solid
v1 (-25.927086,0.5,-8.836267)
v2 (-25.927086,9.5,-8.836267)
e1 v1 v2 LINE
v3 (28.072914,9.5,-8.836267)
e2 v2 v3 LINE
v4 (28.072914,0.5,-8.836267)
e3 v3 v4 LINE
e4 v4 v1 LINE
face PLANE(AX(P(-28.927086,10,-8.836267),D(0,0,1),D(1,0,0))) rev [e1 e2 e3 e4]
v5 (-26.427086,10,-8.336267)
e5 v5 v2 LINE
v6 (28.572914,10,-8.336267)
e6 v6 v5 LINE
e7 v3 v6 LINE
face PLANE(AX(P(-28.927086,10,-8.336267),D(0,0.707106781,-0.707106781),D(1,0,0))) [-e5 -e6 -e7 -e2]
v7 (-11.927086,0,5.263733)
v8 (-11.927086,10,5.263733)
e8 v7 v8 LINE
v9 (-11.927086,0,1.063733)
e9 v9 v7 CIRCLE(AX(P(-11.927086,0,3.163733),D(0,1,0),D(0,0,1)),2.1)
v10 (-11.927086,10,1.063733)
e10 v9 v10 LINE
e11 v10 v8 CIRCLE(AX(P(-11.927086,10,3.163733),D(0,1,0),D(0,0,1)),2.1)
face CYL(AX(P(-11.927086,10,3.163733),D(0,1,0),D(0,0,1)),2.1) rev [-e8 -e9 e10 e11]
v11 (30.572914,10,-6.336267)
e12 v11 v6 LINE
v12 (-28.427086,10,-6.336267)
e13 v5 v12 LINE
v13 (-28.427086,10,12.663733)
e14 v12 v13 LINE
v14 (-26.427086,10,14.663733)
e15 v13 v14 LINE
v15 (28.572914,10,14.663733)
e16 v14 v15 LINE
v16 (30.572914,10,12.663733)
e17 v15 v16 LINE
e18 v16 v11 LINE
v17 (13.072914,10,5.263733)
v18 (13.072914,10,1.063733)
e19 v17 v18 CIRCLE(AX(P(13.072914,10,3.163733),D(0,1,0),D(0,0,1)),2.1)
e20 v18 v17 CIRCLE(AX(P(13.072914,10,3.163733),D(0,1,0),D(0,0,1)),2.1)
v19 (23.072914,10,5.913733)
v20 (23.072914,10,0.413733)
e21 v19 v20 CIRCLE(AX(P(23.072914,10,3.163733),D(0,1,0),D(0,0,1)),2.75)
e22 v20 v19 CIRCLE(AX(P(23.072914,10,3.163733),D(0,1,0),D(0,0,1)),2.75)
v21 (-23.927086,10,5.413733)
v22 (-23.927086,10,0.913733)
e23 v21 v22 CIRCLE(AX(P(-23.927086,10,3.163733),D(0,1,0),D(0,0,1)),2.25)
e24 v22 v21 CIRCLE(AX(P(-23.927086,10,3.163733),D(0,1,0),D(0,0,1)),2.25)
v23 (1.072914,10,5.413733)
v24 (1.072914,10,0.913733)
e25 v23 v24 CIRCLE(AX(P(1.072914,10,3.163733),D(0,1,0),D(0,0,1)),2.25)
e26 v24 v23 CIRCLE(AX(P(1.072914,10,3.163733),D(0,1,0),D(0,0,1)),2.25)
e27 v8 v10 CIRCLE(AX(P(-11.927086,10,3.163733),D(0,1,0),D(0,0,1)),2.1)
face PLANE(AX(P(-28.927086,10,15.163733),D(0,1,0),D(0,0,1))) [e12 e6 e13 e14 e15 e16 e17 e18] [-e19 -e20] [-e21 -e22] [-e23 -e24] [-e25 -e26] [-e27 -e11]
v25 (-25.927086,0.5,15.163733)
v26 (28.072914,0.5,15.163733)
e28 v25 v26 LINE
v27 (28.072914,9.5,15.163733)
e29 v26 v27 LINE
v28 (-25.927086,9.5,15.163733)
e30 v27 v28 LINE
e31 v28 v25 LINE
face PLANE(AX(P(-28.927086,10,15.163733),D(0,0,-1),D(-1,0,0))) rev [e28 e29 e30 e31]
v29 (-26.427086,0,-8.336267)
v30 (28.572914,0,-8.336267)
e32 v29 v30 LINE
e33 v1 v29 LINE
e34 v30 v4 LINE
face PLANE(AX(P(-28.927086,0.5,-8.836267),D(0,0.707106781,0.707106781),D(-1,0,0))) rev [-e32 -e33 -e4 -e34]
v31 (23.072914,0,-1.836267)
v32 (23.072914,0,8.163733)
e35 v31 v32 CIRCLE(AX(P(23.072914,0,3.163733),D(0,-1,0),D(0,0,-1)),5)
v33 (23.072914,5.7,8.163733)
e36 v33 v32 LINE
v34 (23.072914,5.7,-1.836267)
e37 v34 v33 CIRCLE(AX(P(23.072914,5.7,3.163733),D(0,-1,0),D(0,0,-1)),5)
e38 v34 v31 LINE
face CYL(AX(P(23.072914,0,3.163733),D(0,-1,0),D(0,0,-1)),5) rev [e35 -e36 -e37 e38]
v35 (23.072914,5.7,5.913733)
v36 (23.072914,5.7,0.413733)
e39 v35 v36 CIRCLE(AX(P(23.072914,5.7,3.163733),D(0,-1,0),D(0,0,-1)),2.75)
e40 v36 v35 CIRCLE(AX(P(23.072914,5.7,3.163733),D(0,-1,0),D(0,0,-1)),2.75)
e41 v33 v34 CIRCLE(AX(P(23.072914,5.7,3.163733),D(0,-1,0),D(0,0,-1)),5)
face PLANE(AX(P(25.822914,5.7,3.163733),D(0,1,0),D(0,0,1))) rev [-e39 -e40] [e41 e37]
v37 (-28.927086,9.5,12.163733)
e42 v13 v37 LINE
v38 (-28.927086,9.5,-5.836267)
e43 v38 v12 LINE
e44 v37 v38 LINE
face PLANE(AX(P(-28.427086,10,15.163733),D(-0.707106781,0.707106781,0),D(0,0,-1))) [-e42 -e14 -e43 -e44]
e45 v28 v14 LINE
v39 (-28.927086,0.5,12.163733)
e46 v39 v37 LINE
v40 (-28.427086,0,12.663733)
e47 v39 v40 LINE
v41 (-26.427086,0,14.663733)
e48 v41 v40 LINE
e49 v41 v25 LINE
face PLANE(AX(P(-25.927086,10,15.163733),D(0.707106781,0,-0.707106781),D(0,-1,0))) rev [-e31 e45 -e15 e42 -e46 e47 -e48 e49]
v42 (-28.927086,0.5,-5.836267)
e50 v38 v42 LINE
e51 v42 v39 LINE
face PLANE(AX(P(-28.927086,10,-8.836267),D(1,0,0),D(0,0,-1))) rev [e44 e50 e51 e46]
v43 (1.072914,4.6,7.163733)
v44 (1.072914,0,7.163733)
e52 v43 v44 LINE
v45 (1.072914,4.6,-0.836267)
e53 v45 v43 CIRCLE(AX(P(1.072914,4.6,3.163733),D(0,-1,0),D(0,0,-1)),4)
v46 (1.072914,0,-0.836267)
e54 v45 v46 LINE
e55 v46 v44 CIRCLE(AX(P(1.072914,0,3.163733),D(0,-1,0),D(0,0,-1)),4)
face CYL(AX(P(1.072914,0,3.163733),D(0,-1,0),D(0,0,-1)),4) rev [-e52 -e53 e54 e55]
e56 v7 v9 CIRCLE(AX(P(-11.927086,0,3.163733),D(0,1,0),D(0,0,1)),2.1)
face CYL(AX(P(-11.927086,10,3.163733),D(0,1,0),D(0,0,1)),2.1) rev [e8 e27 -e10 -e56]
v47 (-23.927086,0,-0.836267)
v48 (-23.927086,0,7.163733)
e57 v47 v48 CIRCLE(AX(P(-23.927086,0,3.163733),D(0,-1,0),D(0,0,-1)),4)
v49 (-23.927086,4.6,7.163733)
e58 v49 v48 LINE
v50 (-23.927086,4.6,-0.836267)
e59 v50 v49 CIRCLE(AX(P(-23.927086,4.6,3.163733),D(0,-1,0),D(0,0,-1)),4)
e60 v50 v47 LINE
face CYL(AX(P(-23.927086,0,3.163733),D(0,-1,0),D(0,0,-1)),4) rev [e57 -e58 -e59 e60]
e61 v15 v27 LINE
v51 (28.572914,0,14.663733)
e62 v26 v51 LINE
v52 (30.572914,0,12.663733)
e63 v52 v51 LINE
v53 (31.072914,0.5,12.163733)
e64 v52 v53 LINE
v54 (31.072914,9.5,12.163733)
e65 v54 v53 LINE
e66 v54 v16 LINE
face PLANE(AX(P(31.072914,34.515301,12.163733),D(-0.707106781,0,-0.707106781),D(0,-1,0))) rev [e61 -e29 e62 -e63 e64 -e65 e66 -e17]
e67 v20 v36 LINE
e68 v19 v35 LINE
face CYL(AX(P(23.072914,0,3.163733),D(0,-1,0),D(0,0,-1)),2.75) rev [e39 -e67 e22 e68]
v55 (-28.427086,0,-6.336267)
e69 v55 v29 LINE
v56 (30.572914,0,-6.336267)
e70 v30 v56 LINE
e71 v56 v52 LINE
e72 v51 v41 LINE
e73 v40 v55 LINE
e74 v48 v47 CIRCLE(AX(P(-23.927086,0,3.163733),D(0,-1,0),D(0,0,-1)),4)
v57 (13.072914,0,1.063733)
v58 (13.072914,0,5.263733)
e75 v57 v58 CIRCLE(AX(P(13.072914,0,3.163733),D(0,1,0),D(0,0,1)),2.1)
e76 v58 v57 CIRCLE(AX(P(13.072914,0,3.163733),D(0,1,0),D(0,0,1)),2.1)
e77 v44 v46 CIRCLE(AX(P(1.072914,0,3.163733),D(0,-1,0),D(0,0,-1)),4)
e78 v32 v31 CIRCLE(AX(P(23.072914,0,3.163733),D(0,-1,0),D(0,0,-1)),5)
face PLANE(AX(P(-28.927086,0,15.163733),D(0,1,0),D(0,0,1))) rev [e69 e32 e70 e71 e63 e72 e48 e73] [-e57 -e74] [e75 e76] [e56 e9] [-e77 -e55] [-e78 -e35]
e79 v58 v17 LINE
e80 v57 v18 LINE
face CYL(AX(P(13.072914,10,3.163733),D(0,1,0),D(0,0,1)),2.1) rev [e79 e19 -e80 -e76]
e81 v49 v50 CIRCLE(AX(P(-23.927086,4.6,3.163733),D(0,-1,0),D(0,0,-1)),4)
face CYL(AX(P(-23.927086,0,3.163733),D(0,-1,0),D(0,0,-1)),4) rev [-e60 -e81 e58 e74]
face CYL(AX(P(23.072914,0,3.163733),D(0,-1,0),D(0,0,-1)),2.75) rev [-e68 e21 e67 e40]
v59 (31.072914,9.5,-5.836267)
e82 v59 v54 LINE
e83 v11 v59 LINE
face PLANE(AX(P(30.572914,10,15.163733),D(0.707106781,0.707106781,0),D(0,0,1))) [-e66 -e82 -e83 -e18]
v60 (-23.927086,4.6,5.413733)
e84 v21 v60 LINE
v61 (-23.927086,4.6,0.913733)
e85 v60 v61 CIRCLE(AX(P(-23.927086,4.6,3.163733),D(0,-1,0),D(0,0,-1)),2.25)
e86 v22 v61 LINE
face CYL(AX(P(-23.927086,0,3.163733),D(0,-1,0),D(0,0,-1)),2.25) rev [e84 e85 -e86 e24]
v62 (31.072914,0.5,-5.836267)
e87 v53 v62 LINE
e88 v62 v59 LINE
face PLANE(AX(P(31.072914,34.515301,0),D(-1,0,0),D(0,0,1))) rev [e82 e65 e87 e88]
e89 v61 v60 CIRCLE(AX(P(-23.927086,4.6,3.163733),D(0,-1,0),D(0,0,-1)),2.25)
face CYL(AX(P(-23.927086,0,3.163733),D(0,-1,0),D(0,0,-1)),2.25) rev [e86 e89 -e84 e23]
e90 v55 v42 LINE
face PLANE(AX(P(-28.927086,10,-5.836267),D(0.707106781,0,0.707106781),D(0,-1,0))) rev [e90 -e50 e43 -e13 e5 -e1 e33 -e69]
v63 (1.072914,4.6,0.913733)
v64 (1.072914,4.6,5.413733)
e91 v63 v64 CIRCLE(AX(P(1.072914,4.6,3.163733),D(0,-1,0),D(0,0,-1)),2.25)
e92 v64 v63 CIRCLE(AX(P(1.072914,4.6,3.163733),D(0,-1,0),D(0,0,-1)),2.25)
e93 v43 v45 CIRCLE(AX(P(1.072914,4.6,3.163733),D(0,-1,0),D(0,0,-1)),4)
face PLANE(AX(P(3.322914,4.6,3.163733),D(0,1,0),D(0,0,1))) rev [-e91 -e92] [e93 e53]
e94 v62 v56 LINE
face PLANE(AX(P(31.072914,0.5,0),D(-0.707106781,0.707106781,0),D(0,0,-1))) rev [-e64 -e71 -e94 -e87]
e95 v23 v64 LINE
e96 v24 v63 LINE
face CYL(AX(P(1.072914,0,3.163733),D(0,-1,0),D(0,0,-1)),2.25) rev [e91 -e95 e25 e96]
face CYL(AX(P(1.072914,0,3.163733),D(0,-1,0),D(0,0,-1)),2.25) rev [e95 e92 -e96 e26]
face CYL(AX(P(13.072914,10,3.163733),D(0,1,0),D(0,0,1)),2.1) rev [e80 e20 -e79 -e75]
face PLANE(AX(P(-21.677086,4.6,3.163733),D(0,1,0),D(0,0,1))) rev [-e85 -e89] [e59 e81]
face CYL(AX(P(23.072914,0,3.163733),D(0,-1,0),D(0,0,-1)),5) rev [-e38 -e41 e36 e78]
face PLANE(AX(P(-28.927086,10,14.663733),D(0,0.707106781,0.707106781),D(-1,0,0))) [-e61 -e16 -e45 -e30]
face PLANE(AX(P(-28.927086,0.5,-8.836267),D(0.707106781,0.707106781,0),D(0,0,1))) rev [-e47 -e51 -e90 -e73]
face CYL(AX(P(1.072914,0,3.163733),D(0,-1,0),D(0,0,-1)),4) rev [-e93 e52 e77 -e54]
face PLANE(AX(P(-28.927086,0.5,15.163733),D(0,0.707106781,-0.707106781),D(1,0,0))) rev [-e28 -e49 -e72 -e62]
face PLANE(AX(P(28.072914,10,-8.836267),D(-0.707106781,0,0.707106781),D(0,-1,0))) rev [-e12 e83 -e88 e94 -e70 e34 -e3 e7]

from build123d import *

# Parameters (mm, degrees)
SKETCH1_W                                          = 55
SKETCH1_H                                          = 24
BOSS_EXTRUDE1_DEPTH                                = 10
HOLE_WIZARD_3_D                                    = 4.5
HOLE_WIZARD_3_DEPTH                                = 12.4
HOLE_WIZARD_3_CBORE_D                              = 8
HOLE_WIZARD_3_CBORE_DEPTH                          = 4.6
HOLE_WIZARD_3_TIP                                  = 1.351936393
SKETCH6_W                                          = 5
SKETCH6_H                                          = 24
BOSS_EXTRUDE2_DEPTH                                = 10
CHAMFER1_SIZE                                      = 3
CHAMFER2_SIZE                                      = 0.5
HOLE_SIZE_BASED_ON_SOCKET_HEAD_CAP_SCR_D           = 5.5
HOLE_SIZE_BASED_ON_SOCKET_HEAD_CAP_SCR_DEPTH       = 12.4
HOLE_SIZE_BASED_ON_SOCKET_HEAD_CAP_SCR_CBORE_D     = 10
HOLE_SIZE_BASED_ON_SOCKET_HEAD_CAP_SCR_CBORE_DEPTH = 5.7
HOLE_SIZE_BASED_ON_SOCKET_HEAD_CAP_SCR_TIP         = 1.652366702
M5_TAPPED_HOLE1_D                                  = 4.2


with BuildPart() as part:
    # Sketch1 → Boss-Extrude1 (new body)
    with BuildSketch(Plane(origin=(0, 0, 0), x_dir=(1, 0, 0), z_dir=(0, 1, 0))):
        with Locations((-1.42708605, -3.163732927)):
            Rectangle(SKETCH1_W, SKETCH1_H)
    extrude(amount=BOSS_EXTRUDE1_DEPTH)

    # 打孔尺寸(%根据)内六角圆柱头螺钉的类型3
    with Locations(Plane(origin=(0, 0, 0), x_dir=(-1, 0, 0), z_dir=(0, -1, 0))):
        with Locations((23.92708605, -3.163732927), (-1.07291395, -3.163732927)):
            CounterBoreHole(HOLE_WIZARD_3_D / 2, HOLE_WIZARD_3_CBORE_D / 2, HOLE_WIZARD_3_CBORE_DEPTH, depth=HOLE_WIZARD_3_DEPTH)
            with Locations((0, 0, -(HOLE_WIZARD_3_DEPTH + HOLE_WIZARD_3_TIP / 2))):  # 118° drill point
                Cone(0, HOLE_WIZARD_3_D / 2, HOLE_WIZARD_3_TIP, mode=Mode.SUBTRACT)

    # Sketch6 → Boss-Extrude2 (add)
    with BuildSketch(Plane.XZ):
        with Locations((28.57291395, 3.163732927)):
            Rectangle(SKETCH6_W, SKETCH6_H)
    extrude(amount=-BOSS_EXTRUDE2_DEPTH)

    # Chamfer1
    chamfer1_edges = [part.edges().sort_by_distance(p)[0] for p in [
        (31.07291395, 5, 15.163732927),
        (31.07291395, 5, -8.836267073),
        (-28.92708605, 5, -8.836267073),
        (-28.92708605, 5, 15.163732927),
    ]]
    chamfer(chamfer1_edges, length=CHAMFER1_SIZE)

    # Chamfer2
    chamfer2_edges = [part.edges().sort_by_distance(p)[0] for p in [
        (1.07291395, 0, -8.836267073),
        (1.07291395, 10, -8.836267073),
        (-28.92708605, 0, 3.163732927),
        (31.07291395, 0, 3.163732927),
        (1.07291395, 0, 15.163732927),
        (31.07291395, 10, 3.163732927),
        (-28.92708605, 10, 3.163732927),
        (1.07291395, 10, 15.163732927),
    ]]
    chamfer(chamfer2_edges, length=CHAMFER2_SIZE)

    # Hole Size _Based On_ Socket Head Cap Scr
    with Locations(Plane(origin=(0, 0, 0), x_dir=(-1, 0, 0), z_dir=(0, -1, 0))):
        with Locations((-23.07291395, -3.163732927)):
            CounterBoreHole(HOLE_SIZE_BASED_ON_SOCKET_HEAD_CAP_SCR_D / 2, HOLE_SIZE_BASED_ON_SOCKET_HEAD_CAP_SCR_CBORE_D / 2, HOLE_SIZE_BASED_ON_SOCKET_HEAD_CAP_SCR_CBORE_DEPTH, depth=HOLE_SIZE_BASED_ON_SOCKET_HEAD_CAP_SCR_DEPTH)
            with Locations((0, 0, -(HOLE_SIZE_BASED_ON_SOCKET_HEAD_CAP_SCR_DEPTH + HOLE_SIZE_BASED_ON_SOCKET_HEAD_CAP_SCR_TIP / 2))):  # 118° drill point
                Cone(0, HOLE_SIZE_BASED_ON_SOCKET_HEAD_CAP_SCR_D / 2, HOLE_SIZE_BASED_ON_SOCKET_HEAD_CAP_SCR_TIP, mode=Mode.SUBTRACT)

    # M5 Tapped Hole1 (through all)
    with Locations(Plane(origin=(0, 10, 0), x_dir=(1, 0, 0), z_dir=(0, 1, 0))):
        with Locations((-11.92708605, -3.163732927), (13.07291395, -3.163732927)):
            Hole(M5_TAPPED_HOLE1_D / 2)


solid = part.part
